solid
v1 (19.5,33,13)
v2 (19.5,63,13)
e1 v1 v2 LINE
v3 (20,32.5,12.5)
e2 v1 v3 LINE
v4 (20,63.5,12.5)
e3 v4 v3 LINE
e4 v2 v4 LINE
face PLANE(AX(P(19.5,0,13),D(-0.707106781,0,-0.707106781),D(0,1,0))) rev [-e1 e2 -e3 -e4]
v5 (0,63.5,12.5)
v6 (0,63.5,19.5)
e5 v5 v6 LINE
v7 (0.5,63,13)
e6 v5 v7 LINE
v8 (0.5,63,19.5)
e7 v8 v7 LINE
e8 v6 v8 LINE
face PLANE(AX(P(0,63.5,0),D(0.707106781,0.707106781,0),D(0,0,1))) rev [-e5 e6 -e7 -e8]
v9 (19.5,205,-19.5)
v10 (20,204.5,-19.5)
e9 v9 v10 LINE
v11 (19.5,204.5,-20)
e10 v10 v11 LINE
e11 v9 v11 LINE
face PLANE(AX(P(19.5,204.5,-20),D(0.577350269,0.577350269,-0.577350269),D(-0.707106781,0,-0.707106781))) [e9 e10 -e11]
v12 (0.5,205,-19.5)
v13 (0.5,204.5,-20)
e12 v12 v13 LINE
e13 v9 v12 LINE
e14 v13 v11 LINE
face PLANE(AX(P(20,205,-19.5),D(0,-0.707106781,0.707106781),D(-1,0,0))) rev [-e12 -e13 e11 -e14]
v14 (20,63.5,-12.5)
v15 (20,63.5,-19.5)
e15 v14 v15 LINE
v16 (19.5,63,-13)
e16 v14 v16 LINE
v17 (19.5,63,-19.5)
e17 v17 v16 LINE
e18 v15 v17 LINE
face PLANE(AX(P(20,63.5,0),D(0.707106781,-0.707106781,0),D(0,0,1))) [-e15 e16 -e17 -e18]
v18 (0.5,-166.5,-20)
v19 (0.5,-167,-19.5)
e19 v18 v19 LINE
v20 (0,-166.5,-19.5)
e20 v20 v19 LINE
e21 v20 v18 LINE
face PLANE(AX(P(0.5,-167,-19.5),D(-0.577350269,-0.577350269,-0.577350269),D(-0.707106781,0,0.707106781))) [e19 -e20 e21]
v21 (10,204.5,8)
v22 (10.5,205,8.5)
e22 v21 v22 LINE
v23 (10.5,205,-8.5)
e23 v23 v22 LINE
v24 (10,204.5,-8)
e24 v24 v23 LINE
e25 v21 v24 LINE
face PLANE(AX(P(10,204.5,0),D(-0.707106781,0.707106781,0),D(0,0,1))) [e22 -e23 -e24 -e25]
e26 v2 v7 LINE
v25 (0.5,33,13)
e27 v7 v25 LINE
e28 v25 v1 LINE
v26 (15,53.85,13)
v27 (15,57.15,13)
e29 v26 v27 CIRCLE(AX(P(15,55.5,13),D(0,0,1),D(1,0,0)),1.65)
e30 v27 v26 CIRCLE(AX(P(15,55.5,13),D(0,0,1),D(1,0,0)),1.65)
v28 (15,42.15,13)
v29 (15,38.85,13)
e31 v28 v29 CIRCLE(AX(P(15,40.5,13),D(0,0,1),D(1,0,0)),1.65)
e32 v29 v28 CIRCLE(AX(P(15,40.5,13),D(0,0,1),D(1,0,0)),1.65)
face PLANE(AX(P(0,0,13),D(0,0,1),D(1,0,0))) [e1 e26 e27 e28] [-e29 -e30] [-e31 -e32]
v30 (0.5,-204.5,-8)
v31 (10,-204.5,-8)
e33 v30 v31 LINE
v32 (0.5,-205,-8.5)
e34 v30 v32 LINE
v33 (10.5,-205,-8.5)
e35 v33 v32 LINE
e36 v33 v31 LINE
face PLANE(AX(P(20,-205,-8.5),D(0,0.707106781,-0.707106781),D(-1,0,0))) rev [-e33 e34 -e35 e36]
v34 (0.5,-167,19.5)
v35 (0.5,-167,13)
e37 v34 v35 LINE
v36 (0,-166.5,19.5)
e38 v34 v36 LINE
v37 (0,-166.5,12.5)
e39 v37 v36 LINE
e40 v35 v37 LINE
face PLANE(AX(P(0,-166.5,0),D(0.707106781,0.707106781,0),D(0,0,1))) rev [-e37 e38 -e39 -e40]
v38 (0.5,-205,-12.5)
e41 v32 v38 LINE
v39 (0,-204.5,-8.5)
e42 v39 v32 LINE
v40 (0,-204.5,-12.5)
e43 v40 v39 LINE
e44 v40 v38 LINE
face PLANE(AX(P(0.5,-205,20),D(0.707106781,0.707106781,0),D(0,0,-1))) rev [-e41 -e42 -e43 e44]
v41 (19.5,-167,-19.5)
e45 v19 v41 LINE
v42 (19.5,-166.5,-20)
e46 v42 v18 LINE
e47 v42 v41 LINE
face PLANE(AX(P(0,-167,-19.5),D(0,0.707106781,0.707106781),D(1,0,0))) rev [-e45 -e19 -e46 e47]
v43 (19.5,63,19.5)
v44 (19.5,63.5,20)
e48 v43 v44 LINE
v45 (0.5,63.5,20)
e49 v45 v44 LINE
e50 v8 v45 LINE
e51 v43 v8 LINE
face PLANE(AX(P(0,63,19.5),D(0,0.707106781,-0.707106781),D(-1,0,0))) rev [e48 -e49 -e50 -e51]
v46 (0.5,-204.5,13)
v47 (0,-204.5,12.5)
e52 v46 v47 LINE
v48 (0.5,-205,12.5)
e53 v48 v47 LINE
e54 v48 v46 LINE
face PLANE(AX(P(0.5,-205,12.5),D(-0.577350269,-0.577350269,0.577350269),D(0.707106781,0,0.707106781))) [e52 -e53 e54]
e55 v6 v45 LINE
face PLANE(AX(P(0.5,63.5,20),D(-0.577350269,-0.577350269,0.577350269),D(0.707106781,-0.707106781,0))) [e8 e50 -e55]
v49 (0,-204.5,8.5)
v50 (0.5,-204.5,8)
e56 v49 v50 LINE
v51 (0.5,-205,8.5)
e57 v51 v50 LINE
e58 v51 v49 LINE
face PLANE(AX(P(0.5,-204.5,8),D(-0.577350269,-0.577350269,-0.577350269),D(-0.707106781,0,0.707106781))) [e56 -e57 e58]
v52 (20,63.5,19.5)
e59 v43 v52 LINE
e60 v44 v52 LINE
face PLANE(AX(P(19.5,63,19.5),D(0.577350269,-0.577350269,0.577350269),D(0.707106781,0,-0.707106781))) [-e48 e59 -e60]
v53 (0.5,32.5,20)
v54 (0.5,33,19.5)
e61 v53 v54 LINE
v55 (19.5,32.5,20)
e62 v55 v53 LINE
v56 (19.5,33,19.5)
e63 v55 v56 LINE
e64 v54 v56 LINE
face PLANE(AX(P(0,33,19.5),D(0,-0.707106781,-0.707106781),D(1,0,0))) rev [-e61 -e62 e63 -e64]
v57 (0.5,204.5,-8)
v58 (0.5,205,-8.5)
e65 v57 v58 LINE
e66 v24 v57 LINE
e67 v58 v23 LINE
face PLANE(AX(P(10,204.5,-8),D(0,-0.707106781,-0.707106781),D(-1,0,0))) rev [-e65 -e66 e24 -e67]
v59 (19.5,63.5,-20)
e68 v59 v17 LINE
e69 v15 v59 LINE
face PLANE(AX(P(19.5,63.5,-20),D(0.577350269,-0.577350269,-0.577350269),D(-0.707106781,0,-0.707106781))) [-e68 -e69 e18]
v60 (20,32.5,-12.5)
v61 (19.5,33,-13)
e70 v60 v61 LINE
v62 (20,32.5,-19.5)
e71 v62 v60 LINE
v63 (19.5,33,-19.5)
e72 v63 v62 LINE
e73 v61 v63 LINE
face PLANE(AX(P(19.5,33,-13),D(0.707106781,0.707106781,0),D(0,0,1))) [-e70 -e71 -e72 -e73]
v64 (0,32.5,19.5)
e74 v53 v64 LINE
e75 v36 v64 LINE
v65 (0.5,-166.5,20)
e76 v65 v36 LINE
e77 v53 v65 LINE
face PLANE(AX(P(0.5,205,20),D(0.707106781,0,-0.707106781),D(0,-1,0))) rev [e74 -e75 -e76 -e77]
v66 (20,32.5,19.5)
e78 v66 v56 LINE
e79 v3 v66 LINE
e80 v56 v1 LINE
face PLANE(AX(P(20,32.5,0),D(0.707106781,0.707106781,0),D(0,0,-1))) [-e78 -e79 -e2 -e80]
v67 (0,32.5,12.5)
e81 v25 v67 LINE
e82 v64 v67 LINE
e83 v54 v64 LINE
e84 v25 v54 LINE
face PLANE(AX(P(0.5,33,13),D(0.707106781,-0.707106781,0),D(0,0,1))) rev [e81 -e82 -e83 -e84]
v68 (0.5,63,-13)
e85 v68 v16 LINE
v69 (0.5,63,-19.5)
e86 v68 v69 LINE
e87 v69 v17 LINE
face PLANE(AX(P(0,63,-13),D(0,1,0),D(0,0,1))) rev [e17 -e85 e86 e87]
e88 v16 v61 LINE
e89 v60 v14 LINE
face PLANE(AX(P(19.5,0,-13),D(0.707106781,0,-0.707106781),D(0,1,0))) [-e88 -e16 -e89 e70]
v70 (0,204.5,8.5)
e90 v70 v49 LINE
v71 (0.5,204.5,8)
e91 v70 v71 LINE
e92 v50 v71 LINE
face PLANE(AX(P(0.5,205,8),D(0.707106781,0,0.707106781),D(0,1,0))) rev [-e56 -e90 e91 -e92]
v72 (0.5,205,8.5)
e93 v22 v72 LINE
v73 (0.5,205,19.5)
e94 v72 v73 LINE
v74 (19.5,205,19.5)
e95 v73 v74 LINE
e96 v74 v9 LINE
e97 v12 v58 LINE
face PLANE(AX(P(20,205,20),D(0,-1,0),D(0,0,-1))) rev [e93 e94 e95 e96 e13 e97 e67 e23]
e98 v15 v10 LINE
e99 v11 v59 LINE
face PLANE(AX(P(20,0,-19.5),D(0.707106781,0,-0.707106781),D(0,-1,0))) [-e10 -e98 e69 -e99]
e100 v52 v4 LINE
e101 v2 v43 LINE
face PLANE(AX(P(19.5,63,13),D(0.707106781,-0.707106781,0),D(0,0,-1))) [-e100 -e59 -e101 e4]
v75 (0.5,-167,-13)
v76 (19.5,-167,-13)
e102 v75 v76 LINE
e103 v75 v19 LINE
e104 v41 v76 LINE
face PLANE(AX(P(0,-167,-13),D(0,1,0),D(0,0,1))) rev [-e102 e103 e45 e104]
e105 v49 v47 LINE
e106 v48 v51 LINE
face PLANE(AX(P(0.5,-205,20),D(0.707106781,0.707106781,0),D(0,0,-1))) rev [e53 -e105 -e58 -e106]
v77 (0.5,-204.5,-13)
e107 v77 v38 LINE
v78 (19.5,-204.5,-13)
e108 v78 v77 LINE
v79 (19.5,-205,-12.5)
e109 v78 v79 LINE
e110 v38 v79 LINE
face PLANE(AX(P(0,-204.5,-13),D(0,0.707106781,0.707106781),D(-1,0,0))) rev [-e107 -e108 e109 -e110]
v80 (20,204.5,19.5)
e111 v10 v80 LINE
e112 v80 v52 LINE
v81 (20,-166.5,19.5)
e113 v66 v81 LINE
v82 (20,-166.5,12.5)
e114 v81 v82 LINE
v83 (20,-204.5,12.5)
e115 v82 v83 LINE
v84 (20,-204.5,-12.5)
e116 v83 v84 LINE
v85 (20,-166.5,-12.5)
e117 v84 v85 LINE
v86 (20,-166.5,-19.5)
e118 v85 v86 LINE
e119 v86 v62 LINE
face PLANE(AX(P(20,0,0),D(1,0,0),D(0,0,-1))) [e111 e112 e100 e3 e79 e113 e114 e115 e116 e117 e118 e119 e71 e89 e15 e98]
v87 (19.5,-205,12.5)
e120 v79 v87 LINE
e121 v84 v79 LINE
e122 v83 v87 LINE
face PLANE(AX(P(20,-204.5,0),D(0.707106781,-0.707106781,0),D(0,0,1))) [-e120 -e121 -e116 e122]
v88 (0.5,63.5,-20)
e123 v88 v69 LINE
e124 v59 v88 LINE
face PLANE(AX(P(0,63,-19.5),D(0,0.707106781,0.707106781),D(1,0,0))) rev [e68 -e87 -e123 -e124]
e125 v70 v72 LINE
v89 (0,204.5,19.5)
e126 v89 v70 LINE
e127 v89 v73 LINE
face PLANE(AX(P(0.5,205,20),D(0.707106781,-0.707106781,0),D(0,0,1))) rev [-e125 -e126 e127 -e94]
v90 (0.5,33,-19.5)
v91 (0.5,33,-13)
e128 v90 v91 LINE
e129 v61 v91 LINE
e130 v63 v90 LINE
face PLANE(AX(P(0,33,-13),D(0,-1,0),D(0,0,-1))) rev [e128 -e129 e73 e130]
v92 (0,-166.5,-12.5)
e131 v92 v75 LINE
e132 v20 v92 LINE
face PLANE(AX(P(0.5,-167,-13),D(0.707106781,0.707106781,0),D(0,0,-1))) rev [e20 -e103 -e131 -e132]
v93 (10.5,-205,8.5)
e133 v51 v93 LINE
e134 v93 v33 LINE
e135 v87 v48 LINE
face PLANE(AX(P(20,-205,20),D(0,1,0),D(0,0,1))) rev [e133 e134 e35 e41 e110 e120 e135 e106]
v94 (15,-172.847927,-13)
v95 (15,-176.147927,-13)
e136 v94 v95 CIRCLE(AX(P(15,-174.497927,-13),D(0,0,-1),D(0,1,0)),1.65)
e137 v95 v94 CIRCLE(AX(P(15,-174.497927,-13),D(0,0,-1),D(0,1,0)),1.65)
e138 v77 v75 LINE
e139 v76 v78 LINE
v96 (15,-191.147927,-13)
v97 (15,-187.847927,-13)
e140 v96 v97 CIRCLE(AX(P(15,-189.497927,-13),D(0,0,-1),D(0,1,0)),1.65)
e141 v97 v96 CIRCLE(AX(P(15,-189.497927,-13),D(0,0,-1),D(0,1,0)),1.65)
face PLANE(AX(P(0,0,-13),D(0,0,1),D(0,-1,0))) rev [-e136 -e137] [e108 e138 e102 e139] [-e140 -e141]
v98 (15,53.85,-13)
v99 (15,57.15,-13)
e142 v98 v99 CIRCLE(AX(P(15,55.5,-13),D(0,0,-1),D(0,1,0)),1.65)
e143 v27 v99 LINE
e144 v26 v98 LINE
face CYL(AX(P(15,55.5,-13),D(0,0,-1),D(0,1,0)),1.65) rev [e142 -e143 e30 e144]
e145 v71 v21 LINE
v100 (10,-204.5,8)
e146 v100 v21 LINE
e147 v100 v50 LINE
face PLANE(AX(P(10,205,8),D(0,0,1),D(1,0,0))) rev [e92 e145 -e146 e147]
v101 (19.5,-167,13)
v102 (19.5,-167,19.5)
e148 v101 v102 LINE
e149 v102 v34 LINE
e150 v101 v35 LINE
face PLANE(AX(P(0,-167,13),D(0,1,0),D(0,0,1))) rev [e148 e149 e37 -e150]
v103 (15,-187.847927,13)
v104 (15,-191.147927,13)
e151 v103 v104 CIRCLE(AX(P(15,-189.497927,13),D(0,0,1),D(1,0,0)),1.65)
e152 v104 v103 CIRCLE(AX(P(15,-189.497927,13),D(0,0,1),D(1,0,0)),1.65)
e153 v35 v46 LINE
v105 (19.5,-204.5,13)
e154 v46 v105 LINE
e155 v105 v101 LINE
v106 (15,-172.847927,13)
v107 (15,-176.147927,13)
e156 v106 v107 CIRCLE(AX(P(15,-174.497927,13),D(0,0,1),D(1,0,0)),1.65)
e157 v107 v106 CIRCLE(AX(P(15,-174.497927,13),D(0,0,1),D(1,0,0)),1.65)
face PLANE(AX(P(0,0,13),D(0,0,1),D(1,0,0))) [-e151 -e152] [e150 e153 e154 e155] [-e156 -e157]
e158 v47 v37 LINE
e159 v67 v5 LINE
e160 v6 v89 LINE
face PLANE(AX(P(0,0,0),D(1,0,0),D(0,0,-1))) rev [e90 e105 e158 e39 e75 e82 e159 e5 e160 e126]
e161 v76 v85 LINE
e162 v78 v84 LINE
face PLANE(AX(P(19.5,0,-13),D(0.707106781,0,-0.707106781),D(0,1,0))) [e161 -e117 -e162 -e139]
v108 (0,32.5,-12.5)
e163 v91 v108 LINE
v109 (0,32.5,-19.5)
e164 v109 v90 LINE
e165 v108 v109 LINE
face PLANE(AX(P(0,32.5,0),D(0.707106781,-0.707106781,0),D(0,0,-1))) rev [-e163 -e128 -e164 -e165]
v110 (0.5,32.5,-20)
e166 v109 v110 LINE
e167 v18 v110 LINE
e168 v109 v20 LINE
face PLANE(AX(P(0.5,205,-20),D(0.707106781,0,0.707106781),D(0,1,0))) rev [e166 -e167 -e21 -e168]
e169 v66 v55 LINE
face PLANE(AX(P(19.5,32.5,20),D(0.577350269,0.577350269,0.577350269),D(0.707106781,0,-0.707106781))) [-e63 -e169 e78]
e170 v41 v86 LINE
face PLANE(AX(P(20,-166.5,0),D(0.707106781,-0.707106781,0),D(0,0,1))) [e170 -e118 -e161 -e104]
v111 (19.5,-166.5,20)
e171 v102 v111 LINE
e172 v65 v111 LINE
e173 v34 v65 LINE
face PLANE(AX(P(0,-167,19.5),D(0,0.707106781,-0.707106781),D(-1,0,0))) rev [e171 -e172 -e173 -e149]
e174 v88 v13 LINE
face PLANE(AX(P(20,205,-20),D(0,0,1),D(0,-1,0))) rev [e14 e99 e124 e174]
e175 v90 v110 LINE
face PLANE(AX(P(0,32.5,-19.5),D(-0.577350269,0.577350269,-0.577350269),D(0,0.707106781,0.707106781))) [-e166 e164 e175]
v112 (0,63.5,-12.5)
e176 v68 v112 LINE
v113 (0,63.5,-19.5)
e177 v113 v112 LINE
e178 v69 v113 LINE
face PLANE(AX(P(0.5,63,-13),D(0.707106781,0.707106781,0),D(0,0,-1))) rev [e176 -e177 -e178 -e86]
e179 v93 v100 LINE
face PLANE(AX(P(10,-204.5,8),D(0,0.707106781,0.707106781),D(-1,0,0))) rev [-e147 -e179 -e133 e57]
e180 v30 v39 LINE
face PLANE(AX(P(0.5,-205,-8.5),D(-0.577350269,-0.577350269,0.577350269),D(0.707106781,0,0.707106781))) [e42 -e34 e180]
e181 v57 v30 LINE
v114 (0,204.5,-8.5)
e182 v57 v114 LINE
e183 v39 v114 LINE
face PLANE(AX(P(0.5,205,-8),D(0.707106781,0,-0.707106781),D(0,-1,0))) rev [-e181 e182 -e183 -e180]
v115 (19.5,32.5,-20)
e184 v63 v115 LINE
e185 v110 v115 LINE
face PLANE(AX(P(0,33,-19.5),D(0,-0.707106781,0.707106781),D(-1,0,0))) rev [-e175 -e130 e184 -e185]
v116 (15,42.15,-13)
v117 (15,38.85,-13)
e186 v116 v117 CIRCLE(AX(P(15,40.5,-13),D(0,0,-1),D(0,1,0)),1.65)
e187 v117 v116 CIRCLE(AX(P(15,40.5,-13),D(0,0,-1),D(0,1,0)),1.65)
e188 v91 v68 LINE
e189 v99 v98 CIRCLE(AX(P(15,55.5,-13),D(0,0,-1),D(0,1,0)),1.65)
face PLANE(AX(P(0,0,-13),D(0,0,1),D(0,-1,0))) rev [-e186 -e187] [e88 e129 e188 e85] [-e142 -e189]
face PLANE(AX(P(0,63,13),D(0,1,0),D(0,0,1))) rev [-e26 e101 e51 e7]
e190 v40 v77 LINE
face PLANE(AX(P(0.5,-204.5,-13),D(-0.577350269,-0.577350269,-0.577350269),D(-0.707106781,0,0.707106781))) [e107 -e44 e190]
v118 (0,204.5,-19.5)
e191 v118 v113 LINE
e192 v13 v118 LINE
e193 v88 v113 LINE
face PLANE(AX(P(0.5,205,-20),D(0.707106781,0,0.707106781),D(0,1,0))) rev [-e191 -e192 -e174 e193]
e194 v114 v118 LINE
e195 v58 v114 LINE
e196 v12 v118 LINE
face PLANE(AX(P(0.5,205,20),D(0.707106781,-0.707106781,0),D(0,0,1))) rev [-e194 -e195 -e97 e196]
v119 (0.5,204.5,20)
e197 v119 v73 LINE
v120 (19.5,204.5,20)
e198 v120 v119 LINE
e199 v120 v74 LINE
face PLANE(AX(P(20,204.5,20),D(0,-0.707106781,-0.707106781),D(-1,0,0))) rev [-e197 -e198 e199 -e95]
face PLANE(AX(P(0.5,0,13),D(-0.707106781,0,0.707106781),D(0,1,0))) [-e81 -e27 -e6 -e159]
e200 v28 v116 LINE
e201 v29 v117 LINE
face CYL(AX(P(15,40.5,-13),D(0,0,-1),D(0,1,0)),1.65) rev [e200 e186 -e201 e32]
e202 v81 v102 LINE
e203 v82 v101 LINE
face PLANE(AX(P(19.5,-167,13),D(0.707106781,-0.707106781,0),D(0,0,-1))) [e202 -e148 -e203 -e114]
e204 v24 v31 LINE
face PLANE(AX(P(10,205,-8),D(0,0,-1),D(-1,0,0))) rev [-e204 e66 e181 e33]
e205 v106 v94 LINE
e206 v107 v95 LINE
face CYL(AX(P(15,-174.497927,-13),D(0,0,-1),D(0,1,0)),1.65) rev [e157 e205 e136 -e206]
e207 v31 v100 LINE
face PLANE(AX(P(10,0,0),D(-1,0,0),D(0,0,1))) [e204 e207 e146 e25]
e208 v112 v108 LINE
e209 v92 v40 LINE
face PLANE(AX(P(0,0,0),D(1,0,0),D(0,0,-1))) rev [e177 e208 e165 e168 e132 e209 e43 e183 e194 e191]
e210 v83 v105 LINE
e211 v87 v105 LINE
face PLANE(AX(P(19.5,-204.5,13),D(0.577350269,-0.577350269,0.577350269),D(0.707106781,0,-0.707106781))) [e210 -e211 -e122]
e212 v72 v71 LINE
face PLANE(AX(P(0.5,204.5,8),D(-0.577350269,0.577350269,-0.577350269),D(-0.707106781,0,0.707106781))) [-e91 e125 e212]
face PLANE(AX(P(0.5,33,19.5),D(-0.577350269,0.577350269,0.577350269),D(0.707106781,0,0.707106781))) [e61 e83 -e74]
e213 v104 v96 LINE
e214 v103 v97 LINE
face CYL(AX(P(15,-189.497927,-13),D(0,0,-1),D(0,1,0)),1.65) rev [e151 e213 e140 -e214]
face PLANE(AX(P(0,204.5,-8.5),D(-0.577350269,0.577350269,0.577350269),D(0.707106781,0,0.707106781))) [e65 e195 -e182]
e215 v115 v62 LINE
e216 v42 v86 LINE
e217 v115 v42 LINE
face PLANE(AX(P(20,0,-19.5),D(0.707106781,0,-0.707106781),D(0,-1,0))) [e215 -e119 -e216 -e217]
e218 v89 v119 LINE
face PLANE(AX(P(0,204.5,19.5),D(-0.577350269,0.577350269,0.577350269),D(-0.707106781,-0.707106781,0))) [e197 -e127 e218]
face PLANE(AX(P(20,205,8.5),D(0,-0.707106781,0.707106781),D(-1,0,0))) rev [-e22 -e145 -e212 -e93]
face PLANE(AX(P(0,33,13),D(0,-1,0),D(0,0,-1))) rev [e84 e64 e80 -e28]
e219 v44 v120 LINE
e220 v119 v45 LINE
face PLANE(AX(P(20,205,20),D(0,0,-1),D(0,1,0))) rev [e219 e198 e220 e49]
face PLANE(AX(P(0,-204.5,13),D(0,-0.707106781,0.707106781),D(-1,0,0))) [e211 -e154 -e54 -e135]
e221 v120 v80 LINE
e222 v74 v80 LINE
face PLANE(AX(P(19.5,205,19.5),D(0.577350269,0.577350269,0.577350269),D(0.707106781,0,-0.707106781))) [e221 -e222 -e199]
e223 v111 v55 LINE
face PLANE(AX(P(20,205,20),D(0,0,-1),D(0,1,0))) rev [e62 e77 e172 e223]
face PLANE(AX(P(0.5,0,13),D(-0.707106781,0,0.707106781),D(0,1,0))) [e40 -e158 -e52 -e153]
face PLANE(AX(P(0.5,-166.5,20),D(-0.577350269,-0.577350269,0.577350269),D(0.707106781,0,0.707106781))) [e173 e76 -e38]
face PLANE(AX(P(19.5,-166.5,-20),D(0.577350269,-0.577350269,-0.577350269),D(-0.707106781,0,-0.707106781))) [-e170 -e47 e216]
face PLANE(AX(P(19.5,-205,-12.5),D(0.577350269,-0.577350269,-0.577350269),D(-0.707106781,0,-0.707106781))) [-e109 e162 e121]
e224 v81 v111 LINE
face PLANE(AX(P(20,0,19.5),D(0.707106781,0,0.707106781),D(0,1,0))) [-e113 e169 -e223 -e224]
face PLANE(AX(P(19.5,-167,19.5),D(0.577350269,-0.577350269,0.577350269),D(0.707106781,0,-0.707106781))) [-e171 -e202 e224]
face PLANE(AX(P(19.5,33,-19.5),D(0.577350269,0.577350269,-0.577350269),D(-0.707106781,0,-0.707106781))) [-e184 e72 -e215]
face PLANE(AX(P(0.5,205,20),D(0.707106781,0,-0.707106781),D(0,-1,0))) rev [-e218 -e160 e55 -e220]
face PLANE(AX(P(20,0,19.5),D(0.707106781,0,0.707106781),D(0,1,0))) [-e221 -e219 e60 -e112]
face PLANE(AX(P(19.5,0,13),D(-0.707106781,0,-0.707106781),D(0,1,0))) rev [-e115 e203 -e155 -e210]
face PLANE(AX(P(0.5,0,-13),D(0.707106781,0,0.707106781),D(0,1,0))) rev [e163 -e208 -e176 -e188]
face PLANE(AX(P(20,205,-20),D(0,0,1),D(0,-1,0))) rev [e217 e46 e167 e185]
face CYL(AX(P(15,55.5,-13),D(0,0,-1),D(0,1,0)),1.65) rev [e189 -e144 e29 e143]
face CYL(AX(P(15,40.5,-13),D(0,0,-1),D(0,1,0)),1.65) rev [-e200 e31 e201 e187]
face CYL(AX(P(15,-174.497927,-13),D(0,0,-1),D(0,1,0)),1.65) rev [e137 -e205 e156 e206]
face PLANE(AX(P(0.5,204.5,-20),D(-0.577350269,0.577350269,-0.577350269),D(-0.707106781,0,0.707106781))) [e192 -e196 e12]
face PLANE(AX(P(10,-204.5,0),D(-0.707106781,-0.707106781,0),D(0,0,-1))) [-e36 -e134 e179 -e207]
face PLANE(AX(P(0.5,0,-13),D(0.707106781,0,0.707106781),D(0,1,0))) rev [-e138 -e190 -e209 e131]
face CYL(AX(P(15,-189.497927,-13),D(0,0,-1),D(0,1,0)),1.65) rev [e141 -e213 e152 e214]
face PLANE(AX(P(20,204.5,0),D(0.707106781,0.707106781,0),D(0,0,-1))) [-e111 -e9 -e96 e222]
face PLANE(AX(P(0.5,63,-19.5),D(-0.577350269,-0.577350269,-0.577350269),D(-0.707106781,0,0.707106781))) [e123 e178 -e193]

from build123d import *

# Parameters (mm, degrees)
SKETCH_1_W          = 40
SKETCH_1_H          = 410
EXTRUDE_1_DEPTH     = 20
SKETCH_2_W          = 16
SKETCH_2_H          = 410
CUT_EXTRUDE_1_DEPTH = 10
SKETCH_3_W          = 20
SKETCH_3_H          = 38
SKETCH_3_H_2        = 30
CUT_EXTRUDE_2_DEPTH = 7
SKETCH_4_W          = 20
SKETCH_4_H          = 30
SKETCH_4_H_2        = 38
CUT_EXTRUDE_3_DEPTH = 7
HOLE_WIZARD_M4_1_D  = 3.3
CHAMFER_1_SIZE      = 0.5


with BuildPart() as part:
    # 草图1 → 凸台-拉伸1 (new body)
    with BuildSketch(Plane(origin=(0, 0, 0), x_dir=(0, 0, -1), z_dir=(1, 0, 0))):
        Rectangle(SKETCH_1_W, SKETCH_1_H)
    extrude(amount=EXTRUDE_1_DEPTH)

    # 草图2 → 切除-拉伸1 (cut)
    with BuildSketch(Plane.ZY):
        Rectangle(SKETCH_2_W, SKETCH_2_H)
    extrude(amount=-CUT_EXTRUDE_1_DEPTH, mode=Mode.SUBTRACT)

    # 草图3 → 切除-拉伸2 (cut)
    with BuildSketch(Plane.XY.offset(20)):
        with Locations((10, -186)):
            Rectangle(SKETCH_3_W, SKETCH_3_H)
        with Locations((10, 48)):
            Rectangle(SKETCH_3_W, SKETCH_3_H_2)
    extrude(amount=-CUT_EXTRUDE_2_DEPTH, mode=Mode.SUBTRACT)

    # 草图4 → 切除-拉伸3 (cut)
    with BuildSketch(Plane(origin=(0, 0, -20), x_dir=(-1, 0, 0), z_dir=(0, 0, -1))):
        with Locations((-10, 48)):
            Rectangle(SKETCH_4_W, SKETCH_4_H)
        with Locations((-10, -186)):
            Rectangle(SKETCH_4_W, SKETCH_4_H_2)
    extrude(amount=-CUT_EXTRUDE_3_DEPTH, mode=Mode.SUBTRACT)

    # M4 螺纹孔1 (through all)
    with Locations(Plane(origin=(0, 0, -13), x_dir=(-1, 0, 0), z_dir=(0, 0, -1))):
        with Locations((-15, 55.5), (-15, 40.5), (-15, -174.49792687), (-15, -189.49792687)):
            Hole(HOLE_WIZARD_M4_1_D / 2)

    # 倒角1
    chamfer_1_edges = [part.edges().sort_by_distance(p)[0] for p in [
        (20, 134, 20),
        (0, -205, -10.5),
        (0, 205, 14),
        (5, 205, 8),
        (10, -205, 0),
        (5, -205, 8),
        (5, -205, -8),
        (10, 205, 0),
        (5, 205, -8),
        (0, 0, 8),
        (0, 0, -8),
        (20, -205, 0),
        (0, -205, 10.5),
        (0, -186, 13),
        (0, -167, 16.5),
        (20, -186, 13),
        (20, -167, 16.5),
        (10, -205, 13),
        (10, -167, 20),
        (20, -67, 20),
        (0, -67, 20),
        (0, 48, 13),
        (0, 33, 16.5),
        (0, 63, 16.5),
        (20, 48, 13),
        (20, 63, 16.5),
        (20, 33, 16.5),
        (0, 134, 20),
        (10, 33, 20),
        (10, 63, 20),
        (0, 205, -14),
        (0, 134, -20),
        (20, 134, -20),
        (0, 48, -13),
        (0, 63, -16.5),
        (0, 33, -16.5),
        (20, 48, -13),
        (20, 33, -16.5),
        (20, 63, -16.5),
        (10, 63, -20),
        (10, 33, -20),
        (20, 205, 0),
        (0, -67, -20),
        (20, -67, -20),
        (10, 205, 20),
        (0, -186, -13),
        (0, -167, -16.5),
        (10, 205, -20),
        (10, -205, -13),
        (20, -186, -13),
        (20, -167, -16.5),
        (10, -167, -20),
    ]]
    chamfer(chamfer_1_edges, length=CHAMFER_1_SIZE)


solid = part.part
